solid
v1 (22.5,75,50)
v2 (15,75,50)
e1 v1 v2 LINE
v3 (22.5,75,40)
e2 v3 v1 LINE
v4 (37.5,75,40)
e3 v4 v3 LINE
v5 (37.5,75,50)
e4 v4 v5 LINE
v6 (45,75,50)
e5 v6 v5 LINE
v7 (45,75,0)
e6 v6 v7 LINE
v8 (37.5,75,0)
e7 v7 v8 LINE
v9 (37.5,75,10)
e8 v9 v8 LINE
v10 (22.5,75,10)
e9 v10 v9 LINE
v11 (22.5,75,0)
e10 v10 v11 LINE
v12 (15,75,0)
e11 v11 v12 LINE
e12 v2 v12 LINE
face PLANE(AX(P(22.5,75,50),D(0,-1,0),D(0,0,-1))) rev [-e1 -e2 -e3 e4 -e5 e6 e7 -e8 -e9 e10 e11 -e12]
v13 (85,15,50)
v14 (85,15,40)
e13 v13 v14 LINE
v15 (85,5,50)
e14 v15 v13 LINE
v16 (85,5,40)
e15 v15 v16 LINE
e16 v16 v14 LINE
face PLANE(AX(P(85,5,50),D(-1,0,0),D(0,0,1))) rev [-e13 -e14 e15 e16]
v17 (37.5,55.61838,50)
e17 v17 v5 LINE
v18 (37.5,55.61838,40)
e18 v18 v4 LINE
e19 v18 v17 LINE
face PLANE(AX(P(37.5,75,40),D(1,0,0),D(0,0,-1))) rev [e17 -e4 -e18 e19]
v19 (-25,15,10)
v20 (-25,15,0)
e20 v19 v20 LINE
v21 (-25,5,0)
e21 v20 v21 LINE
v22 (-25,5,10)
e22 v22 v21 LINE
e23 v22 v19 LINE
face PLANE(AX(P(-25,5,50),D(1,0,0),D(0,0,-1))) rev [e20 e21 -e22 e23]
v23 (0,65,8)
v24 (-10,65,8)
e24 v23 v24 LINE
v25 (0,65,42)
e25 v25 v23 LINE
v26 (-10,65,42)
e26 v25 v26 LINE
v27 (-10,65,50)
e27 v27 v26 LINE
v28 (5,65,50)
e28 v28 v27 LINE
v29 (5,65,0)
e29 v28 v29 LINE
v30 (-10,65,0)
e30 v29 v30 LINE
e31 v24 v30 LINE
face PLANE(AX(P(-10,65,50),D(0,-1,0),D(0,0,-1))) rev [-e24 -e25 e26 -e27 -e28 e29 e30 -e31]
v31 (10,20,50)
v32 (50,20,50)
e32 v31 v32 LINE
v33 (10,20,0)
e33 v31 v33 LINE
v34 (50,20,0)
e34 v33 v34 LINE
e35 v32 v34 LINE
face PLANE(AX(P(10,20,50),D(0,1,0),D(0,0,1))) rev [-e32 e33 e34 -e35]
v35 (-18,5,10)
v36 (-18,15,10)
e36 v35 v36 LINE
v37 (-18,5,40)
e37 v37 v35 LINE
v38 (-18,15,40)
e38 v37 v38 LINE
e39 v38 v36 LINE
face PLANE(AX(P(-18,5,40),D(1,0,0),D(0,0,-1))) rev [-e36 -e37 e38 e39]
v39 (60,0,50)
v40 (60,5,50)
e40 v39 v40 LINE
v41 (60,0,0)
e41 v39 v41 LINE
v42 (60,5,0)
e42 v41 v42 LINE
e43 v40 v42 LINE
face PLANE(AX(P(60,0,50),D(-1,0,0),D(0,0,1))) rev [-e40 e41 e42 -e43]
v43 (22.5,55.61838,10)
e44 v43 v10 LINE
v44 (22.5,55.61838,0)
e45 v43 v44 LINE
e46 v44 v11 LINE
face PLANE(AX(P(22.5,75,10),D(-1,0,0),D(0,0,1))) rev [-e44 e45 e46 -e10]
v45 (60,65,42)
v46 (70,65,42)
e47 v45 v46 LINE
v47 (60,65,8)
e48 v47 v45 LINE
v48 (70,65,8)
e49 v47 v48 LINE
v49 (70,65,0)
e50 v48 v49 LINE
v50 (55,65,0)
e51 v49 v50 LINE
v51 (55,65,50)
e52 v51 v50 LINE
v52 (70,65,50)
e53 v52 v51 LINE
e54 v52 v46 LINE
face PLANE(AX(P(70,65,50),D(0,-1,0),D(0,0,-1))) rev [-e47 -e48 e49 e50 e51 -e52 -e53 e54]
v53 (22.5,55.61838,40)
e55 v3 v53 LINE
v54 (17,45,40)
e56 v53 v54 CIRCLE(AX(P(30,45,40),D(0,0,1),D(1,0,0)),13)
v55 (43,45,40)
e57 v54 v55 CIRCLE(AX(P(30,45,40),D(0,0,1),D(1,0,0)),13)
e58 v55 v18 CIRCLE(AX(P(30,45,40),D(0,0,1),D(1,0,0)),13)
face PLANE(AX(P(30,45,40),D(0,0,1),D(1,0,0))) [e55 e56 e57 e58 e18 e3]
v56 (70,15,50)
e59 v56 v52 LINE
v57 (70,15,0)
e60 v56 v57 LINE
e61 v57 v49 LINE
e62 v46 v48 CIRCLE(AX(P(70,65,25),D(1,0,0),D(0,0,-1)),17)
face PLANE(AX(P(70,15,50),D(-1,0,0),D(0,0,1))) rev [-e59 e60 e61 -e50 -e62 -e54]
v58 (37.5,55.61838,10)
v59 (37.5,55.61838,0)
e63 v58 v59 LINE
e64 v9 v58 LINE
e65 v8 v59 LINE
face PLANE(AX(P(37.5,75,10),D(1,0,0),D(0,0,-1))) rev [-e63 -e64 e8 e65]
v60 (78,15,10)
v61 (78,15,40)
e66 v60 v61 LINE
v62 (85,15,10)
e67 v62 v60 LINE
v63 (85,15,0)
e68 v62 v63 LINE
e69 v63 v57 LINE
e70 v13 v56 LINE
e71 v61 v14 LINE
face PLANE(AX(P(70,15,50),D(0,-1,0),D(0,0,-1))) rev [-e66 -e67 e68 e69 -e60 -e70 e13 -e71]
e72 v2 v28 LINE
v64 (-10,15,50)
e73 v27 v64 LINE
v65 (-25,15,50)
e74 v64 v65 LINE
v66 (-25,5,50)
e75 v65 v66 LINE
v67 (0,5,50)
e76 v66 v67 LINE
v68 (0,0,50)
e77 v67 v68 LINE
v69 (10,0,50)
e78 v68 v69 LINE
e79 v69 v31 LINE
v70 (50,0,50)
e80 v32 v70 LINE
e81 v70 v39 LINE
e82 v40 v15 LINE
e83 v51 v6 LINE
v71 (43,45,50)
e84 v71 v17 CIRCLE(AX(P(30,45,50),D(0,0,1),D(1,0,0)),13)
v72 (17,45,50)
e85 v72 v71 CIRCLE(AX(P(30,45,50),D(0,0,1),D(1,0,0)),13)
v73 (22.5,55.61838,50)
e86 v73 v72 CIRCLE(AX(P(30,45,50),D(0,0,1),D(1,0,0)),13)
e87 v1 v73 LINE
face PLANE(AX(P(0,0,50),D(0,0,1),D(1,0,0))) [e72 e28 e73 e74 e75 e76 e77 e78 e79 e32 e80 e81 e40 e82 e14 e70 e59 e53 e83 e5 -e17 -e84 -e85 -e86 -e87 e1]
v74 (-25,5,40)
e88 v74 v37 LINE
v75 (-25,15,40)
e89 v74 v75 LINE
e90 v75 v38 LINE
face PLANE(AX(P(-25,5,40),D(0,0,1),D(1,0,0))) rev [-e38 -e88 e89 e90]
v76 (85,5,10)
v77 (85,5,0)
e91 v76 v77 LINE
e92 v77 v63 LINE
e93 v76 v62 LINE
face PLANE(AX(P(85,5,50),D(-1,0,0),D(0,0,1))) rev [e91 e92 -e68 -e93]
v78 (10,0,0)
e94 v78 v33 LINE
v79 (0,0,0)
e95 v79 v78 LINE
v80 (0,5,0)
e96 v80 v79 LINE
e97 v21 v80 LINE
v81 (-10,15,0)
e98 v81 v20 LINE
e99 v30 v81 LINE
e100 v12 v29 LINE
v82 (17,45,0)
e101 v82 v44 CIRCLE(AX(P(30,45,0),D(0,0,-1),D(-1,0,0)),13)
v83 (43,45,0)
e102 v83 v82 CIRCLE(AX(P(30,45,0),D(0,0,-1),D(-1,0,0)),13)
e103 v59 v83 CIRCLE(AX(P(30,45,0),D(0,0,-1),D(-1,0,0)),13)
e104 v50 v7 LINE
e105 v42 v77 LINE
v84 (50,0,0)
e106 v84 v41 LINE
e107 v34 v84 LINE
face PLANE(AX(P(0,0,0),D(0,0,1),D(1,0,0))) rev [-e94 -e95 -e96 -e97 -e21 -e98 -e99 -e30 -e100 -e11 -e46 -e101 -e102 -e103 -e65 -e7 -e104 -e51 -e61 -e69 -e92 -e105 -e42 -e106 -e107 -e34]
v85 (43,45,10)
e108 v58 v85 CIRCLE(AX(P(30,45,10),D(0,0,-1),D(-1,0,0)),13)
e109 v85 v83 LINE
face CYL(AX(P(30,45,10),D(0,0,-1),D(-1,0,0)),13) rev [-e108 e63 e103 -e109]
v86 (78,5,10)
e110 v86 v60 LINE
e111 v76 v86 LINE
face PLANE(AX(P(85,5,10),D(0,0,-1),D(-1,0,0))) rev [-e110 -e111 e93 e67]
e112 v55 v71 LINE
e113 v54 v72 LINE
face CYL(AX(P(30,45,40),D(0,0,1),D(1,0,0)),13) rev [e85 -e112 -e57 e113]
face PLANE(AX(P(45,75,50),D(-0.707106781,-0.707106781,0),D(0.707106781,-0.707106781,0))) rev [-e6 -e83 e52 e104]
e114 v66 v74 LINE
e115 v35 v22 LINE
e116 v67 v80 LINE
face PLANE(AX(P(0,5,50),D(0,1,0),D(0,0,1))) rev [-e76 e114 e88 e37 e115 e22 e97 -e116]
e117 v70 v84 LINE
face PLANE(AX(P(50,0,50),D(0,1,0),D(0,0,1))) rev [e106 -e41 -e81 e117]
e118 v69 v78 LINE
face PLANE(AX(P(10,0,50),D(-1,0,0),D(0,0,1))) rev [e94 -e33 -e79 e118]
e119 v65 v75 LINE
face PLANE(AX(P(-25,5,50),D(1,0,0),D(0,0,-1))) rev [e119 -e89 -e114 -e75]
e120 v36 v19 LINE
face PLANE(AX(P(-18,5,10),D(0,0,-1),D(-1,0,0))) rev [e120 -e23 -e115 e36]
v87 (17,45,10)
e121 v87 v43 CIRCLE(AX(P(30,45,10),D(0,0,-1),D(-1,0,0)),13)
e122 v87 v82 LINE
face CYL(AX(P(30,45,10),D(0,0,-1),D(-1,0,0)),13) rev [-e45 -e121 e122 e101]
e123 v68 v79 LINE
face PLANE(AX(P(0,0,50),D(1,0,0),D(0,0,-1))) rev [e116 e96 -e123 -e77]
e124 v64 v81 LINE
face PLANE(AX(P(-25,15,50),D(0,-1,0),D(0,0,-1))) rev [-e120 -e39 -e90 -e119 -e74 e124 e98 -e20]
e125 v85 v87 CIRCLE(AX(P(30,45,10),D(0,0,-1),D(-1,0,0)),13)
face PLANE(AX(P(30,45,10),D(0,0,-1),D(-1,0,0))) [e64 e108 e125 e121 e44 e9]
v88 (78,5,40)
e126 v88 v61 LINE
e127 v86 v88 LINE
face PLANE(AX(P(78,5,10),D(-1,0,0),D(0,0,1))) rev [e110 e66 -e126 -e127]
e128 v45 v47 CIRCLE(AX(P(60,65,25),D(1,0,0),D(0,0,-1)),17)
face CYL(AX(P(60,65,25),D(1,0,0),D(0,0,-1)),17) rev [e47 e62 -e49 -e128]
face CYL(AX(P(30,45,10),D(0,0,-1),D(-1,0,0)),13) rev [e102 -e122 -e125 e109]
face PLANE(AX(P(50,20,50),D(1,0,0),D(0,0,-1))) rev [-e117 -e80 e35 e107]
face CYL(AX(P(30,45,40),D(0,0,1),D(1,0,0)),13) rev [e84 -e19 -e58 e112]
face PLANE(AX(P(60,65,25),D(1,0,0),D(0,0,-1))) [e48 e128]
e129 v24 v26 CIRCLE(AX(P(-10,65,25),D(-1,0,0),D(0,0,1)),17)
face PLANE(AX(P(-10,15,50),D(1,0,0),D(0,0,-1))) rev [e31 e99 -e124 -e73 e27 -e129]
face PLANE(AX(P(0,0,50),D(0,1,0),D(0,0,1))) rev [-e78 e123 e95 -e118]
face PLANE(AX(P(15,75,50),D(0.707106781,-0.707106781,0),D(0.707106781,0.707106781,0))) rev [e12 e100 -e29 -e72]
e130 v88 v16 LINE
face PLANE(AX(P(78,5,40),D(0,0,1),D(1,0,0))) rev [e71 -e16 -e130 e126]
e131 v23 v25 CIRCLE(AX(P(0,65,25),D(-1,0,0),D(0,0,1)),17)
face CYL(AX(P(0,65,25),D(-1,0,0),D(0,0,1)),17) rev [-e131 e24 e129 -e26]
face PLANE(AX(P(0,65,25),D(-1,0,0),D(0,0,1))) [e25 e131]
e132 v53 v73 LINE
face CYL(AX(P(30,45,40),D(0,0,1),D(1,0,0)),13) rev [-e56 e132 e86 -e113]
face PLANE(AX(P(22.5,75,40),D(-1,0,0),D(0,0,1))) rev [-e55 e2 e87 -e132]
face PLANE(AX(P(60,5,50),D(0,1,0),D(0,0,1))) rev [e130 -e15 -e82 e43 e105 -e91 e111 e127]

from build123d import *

# Parameters (mm, degrees)
MAIN_BODY_50MM_DEPTH     = 50
BEARING_SEAT_CUT_1_DEPTH = 10
BEARING_START            = -10
BEARING_SEAT_CUT_2_DEPTH = 10
TOP_GROOVE_CUT_1_DEPTH   = 10
TOP_START                = -10
TOP_GROOVE_CUT_2_DEPTH   = 10
BASE_NOTCH_1_SKETCH_W    = 7
BASE_NOTCH_1_SKETCH_H    = 30
BASE_NOTCH_CUT_1_DEPTH   = 10
BASE_NOTCH_2_SKETCH_W    = 7
BASE_NOTCH_2_SKETCH_H    = 30
BASE_NOTCH_CUT_2_DEPTH   = 10


with BuildPart() as part:
    # Body Profile Sketch → Main Body 50mm (new body)
    with BuildSketch(Plane.XY):
        Polygon((0, 0), (0, 5), (-25, 5), (-25, 15), (-10, 15), (-10, 65), (5, 65), (15, 75), (22.5, 75), (30, 75), (37.5, 75), (45, 75), (55, 65), (70, 65), (70, 15), (85, 15), (85, 5), (60, 5), (60, 0), (50, 0), (50, 20), (10, 20), (10, 0), align=None)
    extrude(amount=MAIN_BODY_50MM_DEPTH)

    # Bearing Seat 1 Sketch → Bearing Seat Cut 1 (cut)
    with BuildSketch(Plane.ZY.offset(10)):
        with BuildLine():
            Line((8, 65), (42, 65))
            ThreePointArc((42, 65), (25, 48), (8, 65))
        make_face()
    extrude(amount=-BEARING_SEAT_CUT_1_DEPTH, mode=Mode.SUBTRACT)

    # Bearing Seat 2 Sketch → Bearing Seat Cut 2 (cut)
    with BuildSketch(Plane(origin=(70, 0, 0), x_dir=(0, 0, -1), z_dir=(1, 0, 0)).offset(BEARING_START)):
        with BuildLine():
            Line((-42, 65), (-8, 65))
            ThreePointArc((-8, 65), (-25, 48), (-42, 65))
        make_face()
    extrude(amount=BEARING_SEAT_CUT_2_DEPTH, mode=Mode.SUBTRACT)

    # Top Groove 1 Sketch → Top Groove Cut 1 (cut)
    with BuildSketch(Plane(origin=(0, 0, 0), x_dir=(-1, 0, 0), z_dir=(0, 0, -1))):
        with BuildLine():
            Line((-30, 75), (-37.5, 75))
            Line((-37.5, 75), (-37.5, 55.618380291))
            ThreePointArc((-37.5, 55.618380291), (-30, 32), (-22.5, 55.618380291))
            Line((-22.5, 55.618380291), (-22.5, 75))
            Line((-22.5, 75), (-30, 75))
        make_face()
    extrude(amount=-TOP_GROOVE_CUT_1_DEPTH, mode=Mode.SUBTRACT)

    # Top Groove 2 Sketch → Top Groove Cut 2 (cut)
    with BuildSketch(Plane.XY.offset(50).offset(TOP_START)):
        with BuildLine():
            Line((30, 75), (22.5, 75))
            Line((22.5, 75), (22.5, 55.618380291))
            ThreePointArc((22.5, 55.618380291), (30, 32), (37.5, 55.618380291))
            Line((37.5, 55.618380291), (37.5, 75))
            Line((37.5, 75), (30, 75))
        make_face()
    extrude(amount=TOP_GROOVE_CUT_2_DEPTH, mode=Mode.SUBTRACT)

    # Base Notch 1 Sketch → Base Notch Cut 1 (cut)
    with BuildSketch(Plane(origin=(0, 15, 0), x_dir=(1, 0, 0), z_dir=(0, 1, 0))):
        with Locations((-21.5, -25)):
            Rectangle(BASE_NOTCH_1_SKETCH_W, BASE_NOTCH_1_SKETCH_H)
    extrude(amount=-BASE_NOTCH_CUT_1_DEPTH, mode=Mode.SUBTRACT)

    # Base Notch 2 Sketch → Base Notch Cut 2 (cut)
    with BuildSketch(Plane(origin=(0, 15, 0), x_dir=(1, 0, 0), z_dir=(0, 1, 0))):
        with Locations((81.5, -25)):
            Rectangle(BASE_NOTCH_2_SKETCH_W, BASE_NOTCH_2_SKETCH_H)
    extrude(amount=-BASE_NOTCH_CUT_2_DEPTH, mode=Mode.SUBTRACT)


solid = part.part
